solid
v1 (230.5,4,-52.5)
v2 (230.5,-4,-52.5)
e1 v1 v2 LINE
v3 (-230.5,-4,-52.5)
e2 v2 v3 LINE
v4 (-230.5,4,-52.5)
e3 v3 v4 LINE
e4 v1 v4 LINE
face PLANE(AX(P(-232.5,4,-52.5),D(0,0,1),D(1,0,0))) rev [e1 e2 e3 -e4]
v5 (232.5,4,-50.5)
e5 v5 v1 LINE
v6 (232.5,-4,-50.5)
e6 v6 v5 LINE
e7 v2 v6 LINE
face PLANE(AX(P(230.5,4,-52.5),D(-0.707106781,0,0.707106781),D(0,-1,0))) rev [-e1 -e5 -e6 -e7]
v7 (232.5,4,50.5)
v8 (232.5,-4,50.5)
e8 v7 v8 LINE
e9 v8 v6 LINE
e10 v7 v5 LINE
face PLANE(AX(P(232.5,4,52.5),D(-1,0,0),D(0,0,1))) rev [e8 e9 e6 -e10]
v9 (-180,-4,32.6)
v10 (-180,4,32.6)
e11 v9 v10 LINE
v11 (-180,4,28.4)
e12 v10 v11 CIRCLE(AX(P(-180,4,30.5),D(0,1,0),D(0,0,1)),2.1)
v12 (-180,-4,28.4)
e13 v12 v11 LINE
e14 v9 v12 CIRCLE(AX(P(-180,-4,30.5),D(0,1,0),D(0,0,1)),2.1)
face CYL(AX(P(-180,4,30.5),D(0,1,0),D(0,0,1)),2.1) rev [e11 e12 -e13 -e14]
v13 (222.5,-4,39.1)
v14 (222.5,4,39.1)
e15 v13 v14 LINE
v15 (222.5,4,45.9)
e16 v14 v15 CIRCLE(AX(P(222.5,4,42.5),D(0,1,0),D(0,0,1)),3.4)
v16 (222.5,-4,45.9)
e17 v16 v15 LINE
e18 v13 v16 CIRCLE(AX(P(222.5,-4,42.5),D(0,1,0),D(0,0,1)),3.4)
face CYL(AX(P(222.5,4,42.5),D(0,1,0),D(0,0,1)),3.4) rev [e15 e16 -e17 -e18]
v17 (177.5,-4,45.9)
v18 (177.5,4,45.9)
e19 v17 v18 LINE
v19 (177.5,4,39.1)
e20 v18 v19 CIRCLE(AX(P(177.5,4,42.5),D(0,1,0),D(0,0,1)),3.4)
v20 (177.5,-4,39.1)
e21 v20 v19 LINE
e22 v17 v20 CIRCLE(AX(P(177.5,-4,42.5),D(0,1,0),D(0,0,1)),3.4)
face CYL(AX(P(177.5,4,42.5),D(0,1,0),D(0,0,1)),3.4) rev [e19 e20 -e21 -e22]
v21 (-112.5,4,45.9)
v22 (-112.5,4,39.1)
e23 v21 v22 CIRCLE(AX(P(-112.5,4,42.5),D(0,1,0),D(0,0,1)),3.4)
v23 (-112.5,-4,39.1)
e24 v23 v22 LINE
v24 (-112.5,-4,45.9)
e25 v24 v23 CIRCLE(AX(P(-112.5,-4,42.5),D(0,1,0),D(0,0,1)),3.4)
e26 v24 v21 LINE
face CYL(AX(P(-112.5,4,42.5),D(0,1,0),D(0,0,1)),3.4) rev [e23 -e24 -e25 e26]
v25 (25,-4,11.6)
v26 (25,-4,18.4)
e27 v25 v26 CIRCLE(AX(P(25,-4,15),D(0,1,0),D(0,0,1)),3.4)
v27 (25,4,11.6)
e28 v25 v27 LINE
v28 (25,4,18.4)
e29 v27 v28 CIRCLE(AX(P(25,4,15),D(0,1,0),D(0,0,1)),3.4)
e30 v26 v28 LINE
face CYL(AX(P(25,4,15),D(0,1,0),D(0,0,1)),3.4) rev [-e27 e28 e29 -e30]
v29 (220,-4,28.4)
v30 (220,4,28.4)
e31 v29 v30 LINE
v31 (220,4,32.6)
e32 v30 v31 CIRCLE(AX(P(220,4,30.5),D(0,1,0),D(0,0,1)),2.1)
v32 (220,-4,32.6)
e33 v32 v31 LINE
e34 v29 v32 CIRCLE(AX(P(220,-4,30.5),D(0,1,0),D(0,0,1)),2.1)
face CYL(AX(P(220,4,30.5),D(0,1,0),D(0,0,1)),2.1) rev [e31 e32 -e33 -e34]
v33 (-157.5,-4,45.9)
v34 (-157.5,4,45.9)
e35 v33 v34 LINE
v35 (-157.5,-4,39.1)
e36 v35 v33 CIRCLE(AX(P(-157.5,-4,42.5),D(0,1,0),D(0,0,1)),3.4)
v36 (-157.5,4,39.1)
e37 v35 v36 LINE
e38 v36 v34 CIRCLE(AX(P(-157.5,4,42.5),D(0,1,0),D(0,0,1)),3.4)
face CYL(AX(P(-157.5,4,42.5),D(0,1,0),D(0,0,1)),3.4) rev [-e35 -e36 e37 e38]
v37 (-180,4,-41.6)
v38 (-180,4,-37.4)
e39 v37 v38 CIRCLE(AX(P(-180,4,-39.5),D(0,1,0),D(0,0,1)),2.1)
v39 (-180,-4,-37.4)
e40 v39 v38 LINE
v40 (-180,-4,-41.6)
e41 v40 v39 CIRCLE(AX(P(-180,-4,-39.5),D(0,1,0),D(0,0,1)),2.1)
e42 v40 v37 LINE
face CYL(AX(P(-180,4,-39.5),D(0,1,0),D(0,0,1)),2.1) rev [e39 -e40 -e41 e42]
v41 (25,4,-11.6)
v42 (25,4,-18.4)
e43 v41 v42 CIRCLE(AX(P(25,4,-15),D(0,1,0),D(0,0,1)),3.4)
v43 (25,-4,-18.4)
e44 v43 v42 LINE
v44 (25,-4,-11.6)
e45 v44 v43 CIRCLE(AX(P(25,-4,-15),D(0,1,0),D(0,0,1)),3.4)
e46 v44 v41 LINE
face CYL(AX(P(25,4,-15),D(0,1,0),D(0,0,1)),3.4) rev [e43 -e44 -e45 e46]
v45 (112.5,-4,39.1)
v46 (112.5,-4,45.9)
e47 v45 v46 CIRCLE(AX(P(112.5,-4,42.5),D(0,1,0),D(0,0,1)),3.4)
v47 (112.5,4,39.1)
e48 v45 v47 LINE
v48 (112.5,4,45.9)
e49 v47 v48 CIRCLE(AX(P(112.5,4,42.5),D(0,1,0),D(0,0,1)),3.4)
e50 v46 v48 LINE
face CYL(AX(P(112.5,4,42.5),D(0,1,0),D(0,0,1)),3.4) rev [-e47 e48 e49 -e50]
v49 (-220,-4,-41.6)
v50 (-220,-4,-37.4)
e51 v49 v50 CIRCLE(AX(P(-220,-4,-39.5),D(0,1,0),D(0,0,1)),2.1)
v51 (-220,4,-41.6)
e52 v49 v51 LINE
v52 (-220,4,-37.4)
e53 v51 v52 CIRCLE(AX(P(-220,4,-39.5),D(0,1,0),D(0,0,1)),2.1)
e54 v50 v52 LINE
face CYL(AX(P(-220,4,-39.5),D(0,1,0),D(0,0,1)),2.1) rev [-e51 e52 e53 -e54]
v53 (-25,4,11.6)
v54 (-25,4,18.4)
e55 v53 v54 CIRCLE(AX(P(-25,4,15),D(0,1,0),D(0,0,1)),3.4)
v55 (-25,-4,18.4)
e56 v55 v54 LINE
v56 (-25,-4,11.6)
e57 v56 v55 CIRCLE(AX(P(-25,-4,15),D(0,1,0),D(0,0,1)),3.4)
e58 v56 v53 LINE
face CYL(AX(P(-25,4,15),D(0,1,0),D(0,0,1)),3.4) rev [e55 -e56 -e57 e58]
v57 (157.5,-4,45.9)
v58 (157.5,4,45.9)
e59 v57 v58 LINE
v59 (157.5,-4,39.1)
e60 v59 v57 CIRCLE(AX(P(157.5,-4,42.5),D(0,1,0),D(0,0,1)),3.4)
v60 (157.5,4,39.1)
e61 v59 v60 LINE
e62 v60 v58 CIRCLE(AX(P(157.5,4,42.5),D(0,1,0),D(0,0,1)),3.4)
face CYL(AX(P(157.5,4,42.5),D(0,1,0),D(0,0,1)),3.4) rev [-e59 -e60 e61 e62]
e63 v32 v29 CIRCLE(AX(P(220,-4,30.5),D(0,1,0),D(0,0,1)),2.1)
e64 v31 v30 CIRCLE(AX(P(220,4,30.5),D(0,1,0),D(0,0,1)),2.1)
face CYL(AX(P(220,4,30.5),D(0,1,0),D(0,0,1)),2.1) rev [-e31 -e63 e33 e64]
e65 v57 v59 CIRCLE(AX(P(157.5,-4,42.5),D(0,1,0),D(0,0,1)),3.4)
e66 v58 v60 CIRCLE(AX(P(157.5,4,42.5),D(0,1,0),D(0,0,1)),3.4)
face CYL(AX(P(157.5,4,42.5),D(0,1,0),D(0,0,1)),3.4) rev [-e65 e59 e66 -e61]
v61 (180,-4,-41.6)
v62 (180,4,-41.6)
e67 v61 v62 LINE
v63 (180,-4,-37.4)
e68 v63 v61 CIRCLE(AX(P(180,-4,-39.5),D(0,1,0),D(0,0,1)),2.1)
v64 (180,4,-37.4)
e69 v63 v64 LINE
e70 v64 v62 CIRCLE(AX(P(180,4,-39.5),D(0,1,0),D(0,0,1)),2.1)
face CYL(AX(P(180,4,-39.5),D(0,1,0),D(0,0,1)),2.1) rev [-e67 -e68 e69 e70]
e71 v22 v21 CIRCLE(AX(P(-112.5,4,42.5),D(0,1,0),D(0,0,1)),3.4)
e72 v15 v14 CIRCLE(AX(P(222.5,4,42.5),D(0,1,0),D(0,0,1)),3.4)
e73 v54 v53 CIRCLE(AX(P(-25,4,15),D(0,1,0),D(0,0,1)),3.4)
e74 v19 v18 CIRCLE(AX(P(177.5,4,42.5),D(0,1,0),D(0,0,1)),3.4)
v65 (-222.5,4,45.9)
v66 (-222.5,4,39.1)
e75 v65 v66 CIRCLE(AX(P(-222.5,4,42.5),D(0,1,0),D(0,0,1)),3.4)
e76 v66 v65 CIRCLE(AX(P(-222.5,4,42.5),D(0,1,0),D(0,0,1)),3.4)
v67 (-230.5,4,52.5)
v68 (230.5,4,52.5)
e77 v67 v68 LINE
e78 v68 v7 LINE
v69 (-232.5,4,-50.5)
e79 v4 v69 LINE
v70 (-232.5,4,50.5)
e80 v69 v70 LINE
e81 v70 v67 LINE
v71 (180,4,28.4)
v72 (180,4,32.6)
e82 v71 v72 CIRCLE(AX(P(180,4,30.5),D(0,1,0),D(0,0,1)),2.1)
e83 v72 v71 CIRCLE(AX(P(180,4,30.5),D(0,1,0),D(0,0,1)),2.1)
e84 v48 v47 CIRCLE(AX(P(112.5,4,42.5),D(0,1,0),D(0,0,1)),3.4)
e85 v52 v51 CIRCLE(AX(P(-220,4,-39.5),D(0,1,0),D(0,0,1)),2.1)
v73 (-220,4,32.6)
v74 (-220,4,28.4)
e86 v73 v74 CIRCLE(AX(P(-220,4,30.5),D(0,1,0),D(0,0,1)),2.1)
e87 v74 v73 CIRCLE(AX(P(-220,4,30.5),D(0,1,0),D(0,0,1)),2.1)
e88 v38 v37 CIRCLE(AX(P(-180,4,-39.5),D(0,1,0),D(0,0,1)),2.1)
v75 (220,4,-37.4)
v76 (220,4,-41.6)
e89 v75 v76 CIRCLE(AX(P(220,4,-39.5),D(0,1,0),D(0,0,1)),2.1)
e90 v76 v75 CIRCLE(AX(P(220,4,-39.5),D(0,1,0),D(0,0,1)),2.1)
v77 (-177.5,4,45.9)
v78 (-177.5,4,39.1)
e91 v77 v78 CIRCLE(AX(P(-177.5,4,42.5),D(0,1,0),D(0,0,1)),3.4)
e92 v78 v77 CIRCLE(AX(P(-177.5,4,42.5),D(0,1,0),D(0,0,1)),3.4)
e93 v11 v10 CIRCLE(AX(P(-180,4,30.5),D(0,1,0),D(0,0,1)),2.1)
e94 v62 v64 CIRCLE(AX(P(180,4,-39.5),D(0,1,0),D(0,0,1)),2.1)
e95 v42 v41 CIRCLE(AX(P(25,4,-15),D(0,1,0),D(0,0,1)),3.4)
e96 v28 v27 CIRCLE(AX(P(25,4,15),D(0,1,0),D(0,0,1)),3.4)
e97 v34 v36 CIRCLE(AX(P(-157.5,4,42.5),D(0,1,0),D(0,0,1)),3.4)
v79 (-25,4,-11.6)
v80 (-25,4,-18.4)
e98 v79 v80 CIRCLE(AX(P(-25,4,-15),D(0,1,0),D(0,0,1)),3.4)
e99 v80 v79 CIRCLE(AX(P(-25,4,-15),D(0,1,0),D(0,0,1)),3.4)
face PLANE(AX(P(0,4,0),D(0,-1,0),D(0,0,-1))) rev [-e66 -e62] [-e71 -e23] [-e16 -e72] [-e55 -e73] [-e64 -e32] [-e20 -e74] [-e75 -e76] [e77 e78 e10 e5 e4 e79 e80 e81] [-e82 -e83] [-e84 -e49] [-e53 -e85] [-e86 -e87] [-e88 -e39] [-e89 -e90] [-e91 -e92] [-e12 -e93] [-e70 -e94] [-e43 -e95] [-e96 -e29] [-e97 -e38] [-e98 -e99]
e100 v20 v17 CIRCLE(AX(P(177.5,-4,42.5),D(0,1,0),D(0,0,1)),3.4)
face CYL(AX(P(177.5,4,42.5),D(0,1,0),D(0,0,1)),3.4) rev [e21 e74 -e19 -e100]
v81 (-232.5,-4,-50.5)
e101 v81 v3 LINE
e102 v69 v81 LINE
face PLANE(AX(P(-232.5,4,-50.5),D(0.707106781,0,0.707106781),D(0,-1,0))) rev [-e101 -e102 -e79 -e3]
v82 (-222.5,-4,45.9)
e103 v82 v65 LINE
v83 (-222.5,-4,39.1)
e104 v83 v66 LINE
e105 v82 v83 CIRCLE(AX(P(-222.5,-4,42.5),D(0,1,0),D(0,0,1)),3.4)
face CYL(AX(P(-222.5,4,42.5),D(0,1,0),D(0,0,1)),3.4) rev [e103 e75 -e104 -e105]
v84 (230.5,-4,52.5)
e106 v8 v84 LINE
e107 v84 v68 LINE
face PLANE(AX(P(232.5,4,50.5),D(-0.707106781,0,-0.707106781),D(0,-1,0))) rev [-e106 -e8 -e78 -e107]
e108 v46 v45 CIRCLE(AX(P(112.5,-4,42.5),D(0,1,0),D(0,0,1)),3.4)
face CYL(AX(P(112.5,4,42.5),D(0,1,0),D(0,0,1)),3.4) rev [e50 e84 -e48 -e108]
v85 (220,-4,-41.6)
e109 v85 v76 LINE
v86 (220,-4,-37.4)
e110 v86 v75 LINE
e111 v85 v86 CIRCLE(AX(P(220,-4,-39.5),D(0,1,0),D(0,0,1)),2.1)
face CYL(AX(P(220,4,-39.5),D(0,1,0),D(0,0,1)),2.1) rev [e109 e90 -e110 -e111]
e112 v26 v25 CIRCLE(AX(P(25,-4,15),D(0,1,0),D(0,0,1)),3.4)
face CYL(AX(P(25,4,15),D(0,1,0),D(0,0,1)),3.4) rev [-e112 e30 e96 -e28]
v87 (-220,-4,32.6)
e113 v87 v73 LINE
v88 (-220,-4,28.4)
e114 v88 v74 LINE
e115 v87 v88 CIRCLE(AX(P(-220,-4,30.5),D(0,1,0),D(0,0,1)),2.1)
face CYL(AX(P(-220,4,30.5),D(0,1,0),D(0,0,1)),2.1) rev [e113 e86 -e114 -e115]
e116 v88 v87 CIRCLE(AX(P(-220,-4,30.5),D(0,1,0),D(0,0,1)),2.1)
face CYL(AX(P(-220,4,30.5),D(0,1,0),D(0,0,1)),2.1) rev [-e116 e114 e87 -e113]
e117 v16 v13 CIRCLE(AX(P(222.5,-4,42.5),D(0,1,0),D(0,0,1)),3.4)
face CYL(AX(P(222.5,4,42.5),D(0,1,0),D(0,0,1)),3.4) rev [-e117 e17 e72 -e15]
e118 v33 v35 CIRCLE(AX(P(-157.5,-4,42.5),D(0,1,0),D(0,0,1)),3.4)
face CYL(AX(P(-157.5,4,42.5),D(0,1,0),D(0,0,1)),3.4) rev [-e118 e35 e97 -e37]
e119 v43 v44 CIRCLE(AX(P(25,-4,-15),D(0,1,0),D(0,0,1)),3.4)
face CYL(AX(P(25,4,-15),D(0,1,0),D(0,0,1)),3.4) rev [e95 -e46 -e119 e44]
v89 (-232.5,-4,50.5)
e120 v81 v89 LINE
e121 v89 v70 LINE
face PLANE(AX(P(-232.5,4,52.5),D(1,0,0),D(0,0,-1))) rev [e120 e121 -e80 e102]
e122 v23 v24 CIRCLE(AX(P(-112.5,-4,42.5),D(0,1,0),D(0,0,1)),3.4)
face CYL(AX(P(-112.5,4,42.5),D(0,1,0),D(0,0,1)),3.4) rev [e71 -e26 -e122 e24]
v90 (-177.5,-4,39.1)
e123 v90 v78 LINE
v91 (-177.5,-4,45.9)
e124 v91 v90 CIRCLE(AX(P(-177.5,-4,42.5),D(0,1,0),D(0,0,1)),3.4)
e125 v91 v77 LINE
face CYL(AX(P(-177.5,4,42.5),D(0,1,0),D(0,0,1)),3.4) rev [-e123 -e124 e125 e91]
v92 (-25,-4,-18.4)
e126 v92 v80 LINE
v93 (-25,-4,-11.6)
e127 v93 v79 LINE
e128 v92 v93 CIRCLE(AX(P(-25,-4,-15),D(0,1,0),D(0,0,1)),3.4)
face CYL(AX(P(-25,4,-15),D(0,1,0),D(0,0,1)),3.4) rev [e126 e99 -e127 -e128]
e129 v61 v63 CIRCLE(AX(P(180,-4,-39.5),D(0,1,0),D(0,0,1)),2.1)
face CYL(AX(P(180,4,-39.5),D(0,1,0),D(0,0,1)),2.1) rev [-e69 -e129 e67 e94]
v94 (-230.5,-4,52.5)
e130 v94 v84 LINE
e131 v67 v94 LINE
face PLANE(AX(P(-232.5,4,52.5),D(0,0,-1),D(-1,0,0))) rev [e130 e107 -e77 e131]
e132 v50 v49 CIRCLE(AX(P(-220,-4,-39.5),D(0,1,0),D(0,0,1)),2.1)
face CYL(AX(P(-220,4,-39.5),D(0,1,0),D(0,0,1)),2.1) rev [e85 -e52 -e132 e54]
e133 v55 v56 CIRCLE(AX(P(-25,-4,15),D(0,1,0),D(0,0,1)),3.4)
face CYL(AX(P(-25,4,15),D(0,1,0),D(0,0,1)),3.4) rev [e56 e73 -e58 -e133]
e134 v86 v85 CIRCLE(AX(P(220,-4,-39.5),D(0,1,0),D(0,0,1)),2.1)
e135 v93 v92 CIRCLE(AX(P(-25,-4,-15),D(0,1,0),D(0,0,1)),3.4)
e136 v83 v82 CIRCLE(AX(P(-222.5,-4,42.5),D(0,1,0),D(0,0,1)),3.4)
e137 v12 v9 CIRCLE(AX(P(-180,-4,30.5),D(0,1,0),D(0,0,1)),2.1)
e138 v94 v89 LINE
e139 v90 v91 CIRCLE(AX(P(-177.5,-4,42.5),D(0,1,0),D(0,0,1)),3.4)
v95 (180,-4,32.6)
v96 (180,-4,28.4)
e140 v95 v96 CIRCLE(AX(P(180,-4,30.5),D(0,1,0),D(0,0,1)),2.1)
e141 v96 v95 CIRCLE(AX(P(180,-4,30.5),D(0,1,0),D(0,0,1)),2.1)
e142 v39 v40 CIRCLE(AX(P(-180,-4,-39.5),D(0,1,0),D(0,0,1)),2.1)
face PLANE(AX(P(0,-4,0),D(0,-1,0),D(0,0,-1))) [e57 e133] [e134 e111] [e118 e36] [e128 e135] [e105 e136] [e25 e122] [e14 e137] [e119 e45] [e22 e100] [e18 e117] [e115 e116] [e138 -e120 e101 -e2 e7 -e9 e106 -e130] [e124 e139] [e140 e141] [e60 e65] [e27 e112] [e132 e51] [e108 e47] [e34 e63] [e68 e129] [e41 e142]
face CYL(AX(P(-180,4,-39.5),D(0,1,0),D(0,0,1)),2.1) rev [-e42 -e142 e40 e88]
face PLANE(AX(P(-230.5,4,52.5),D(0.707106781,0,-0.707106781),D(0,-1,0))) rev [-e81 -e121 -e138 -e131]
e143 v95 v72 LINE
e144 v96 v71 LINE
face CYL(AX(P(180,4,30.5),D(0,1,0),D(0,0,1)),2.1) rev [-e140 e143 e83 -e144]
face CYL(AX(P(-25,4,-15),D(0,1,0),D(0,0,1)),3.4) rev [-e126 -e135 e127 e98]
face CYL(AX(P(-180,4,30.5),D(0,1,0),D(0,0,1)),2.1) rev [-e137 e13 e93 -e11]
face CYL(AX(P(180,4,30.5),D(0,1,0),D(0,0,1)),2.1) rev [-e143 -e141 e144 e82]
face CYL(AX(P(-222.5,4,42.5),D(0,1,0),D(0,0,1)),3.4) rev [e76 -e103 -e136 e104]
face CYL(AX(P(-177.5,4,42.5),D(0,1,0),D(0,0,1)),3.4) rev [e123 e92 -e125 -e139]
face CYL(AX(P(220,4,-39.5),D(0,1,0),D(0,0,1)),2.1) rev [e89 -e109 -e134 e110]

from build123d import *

# Parameters (mm, degrees)
SKETCH_1_W              = 465
SKETCH_1_H              = 105
EXTRUDE_1_DEPTH         = 4
CHAMFER_1_SIZE          = 2
HOLE_WIZARD_M5_1_D      = 4.2
HOLE_WIZARD_6_8_6_8_1_D = 6.8
HOLE_WIZARD_M8_1_D      = 6.8


with BuildPart() as part:
    # 草图1 → 凸台-拉伸1 (new, symmetric)
    with BuildSketch(Plane(origin=(0, 0, 0), x_dir=(1, 0, 0), z_dir=(0, 1, 0))):
        Rectangle(SKETCH_1_W, SKETCH_1_H)
    extrude(amount=EXTRUDE_1_DEPTH, both=True)

    # 倒角1
    chamfer_1_edges = [part.edges().sort_by_distance(p)[0] for p in [
        (232.5, 0, 52.5),
        (-232.5, 0, 52.5),
        (-232.5, 0, -52.5),
        (232.5, 0, -52.5),
    ]]
    chamfer(chamfer_1_edges, length=CHAMFER_1_SIZE)

    # M5 螺纹孔1 (through all)
    with Locations(Plane(origin=(0, 4, 0), x_dir=(1, 0, 0), z_dir=(0, 1, 0))):
        with Locations((-220, 39.5), (-180, 39.5), (-180, -30.5), (-220, -30.5), (220, -30.5), (180, -30.5), (180, 39.5), (220, 39.5)):
            Hole(HOLE_WIZARD_M5_1_D / 2)

    # Ø6.8 (6.8) 直径孔1 (through all)
    with Locations(Plane(origin=(0, 4, 0), x_dir=(1, 0, 0), z_dir=(0, 1, 0))):
        with Locations((25, -15), (25, 15), (-25, 15), (-25, -15)):
            Hole(HOLE_WIZARD_6_8_6_8_1_D / 2)

    # M8 螺纹孔1 (through all)
    with Locations(Plane(origin=(0, 4, 0), x_dir=(1, 0, 0), z_dir=(0, 1, 0))):
        with Locations((222.5, -42.5), (177.5, -42.5), (-177.5, -42.5), (-222.5, -42.5), (157.5, -42.5), (112.5, -42.5), (-112.5, -42.5), (-157.5, -42.5)):
            Hole(HOLE_WIZARD_M8_1_D / 2)


solid = part.part
